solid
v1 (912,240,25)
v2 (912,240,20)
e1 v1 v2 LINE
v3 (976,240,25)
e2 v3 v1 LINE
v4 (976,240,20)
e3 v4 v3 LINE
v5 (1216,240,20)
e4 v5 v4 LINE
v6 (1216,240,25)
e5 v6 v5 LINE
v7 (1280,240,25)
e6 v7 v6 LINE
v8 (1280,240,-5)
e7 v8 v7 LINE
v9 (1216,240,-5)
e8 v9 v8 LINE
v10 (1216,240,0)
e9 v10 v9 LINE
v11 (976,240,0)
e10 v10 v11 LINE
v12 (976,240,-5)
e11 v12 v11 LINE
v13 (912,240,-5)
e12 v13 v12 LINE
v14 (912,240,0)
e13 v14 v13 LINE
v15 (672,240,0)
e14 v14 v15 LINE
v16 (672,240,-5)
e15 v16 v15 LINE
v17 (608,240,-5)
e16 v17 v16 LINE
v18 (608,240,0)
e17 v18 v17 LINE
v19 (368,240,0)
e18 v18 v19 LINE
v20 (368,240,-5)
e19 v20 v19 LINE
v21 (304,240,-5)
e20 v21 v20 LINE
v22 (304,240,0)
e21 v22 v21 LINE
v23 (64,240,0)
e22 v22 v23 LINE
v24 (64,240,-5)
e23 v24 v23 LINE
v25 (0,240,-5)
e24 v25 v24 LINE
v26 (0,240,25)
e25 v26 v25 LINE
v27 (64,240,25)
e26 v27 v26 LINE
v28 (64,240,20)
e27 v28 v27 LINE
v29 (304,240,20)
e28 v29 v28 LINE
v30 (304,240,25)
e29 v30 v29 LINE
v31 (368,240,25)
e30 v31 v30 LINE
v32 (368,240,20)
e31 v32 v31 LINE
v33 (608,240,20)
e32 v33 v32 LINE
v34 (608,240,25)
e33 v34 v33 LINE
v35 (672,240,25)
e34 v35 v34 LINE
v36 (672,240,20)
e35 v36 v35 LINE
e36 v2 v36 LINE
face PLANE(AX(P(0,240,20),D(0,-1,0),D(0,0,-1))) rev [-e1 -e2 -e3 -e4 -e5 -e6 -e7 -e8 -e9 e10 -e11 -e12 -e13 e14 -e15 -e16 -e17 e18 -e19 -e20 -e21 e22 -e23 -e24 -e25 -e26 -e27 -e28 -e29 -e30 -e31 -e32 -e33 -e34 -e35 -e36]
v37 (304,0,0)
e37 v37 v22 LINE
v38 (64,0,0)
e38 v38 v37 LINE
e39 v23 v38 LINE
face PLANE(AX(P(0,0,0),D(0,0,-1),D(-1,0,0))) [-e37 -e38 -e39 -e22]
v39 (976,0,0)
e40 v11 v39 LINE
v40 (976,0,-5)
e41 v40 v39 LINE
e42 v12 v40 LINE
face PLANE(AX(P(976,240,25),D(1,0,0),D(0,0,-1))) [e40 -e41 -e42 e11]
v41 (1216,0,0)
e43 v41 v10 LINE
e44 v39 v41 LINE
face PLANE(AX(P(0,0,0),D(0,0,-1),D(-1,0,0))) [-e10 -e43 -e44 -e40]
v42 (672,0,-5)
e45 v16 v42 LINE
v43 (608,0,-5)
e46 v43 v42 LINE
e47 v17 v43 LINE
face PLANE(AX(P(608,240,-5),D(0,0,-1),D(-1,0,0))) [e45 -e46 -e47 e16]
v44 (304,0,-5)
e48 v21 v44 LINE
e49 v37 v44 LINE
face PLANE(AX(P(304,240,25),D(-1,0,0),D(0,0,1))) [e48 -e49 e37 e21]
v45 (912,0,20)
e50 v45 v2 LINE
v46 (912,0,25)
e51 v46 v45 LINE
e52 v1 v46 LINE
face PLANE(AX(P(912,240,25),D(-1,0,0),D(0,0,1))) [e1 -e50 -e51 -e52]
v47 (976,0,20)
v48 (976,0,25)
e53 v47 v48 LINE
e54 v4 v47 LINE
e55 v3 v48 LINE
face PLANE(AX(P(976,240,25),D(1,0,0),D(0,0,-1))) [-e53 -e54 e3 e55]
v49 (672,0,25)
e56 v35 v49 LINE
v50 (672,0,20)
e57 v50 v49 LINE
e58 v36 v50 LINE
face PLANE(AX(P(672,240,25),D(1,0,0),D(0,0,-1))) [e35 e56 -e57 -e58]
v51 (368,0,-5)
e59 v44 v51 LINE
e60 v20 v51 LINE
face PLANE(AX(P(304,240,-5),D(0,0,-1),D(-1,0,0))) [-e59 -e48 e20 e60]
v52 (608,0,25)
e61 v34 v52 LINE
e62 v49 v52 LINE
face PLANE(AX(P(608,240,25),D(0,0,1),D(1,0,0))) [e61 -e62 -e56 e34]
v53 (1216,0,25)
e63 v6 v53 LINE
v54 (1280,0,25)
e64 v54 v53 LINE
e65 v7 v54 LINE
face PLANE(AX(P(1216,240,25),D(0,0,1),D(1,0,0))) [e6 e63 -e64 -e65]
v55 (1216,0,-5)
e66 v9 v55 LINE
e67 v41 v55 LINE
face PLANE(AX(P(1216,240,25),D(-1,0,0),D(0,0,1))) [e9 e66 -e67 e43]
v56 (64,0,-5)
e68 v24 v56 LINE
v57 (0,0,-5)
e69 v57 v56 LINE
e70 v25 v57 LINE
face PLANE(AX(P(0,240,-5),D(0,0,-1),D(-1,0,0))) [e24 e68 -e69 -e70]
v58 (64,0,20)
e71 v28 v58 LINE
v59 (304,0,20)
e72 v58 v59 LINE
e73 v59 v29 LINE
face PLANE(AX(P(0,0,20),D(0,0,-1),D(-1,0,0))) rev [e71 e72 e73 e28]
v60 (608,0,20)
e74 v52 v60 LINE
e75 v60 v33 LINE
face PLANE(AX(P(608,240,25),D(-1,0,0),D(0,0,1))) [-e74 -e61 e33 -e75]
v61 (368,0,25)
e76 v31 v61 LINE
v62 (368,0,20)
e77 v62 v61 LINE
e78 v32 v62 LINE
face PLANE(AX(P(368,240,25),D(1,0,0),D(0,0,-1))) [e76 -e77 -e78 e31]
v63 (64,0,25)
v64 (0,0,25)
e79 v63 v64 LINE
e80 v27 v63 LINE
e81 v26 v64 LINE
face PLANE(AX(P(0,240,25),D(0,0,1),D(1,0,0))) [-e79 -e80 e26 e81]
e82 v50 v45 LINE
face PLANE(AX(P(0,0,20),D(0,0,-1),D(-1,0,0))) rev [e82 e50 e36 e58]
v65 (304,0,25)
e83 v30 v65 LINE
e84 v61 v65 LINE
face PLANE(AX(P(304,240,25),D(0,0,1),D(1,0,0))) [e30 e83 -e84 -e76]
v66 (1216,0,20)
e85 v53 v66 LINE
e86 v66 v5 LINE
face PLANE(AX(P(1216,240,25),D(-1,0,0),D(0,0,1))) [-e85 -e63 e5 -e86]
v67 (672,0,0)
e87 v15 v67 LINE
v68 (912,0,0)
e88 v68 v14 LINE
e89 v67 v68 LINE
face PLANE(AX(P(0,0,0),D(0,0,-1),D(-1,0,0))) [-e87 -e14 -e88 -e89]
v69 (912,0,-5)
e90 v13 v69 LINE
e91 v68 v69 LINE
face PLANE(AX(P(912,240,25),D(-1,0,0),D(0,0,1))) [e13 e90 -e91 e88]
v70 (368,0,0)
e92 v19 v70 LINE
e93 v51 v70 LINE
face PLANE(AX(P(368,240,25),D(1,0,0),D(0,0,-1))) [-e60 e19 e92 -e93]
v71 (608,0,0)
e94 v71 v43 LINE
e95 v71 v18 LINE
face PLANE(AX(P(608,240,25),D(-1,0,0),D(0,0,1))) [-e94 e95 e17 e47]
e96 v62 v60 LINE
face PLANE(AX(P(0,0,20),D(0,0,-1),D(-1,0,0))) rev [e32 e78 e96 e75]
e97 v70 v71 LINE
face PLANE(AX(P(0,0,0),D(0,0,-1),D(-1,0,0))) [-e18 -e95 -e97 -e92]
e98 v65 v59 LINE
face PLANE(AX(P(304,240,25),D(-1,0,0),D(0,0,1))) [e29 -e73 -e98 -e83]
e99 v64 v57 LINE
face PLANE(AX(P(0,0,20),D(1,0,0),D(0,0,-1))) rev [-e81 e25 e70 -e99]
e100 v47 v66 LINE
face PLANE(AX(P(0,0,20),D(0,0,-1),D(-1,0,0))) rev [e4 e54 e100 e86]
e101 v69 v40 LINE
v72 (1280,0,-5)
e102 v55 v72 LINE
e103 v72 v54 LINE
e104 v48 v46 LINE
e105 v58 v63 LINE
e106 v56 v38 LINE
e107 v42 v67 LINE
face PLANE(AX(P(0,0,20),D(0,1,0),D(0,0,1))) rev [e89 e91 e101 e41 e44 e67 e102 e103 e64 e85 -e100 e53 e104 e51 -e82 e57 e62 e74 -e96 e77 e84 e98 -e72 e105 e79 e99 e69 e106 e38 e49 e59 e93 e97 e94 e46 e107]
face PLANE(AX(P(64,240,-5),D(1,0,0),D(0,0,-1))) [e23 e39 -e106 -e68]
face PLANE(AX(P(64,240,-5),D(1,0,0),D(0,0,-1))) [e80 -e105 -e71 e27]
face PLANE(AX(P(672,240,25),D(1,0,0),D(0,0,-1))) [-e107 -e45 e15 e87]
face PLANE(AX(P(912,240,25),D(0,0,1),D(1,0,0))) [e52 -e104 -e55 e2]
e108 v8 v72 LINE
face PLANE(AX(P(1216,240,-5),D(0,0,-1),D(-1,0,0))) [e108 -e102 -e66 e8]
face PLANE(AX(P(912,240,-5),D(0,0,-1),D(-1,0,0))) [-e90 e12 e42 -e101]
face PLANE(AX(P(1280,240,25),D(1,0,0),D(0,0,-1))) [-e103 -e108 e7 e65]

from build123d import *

# Parameters (mm, degrees)
SKETCH1_W           = 1270
SKETCH1_H           = 240
BOSS_EXTRUDE1_DEPTH = 20
SKETCH3_W           = 64
SKETCH3_H           = 30
BOSS_EXTRUDE2_DEPTH = 240


with BuildPart() as part:
    # Sketch1 → Boss-Extrude1 (new body)
    with BuildSketch(Plane.XY):
        with Locations((635, 120)):
            Rectangle(SKETCH1_W, SKETCH1_H)
    extrude(amount=BOSS_EXTRUDE1_DEPTH)

    # Sketch3 → Boss-Extrude2 (add)
    with BuildSketch(Plane.XZ):
        with Locations((32, 10)):
            Rectangle(SKETCH3_W, SKETCH3_H)
        with Locations((336, 10)):
            Rectangle(SKETCH3_W, SKETCH3_H)
        with Locations((640, 10)):
            Rectangle(SKETCH3_W, SKETCH3_H)
        with Locations((944, 10)):
            Rectangle(SKETCH3_W, SKETCH3_H)
        with Locations((1248, 10)):
            Rectangle(SKETCH3_W, SKETCH3_H)
    extrude(amount=-BOSS_EXTRUDE2_DEPTH)


solid = part.part
